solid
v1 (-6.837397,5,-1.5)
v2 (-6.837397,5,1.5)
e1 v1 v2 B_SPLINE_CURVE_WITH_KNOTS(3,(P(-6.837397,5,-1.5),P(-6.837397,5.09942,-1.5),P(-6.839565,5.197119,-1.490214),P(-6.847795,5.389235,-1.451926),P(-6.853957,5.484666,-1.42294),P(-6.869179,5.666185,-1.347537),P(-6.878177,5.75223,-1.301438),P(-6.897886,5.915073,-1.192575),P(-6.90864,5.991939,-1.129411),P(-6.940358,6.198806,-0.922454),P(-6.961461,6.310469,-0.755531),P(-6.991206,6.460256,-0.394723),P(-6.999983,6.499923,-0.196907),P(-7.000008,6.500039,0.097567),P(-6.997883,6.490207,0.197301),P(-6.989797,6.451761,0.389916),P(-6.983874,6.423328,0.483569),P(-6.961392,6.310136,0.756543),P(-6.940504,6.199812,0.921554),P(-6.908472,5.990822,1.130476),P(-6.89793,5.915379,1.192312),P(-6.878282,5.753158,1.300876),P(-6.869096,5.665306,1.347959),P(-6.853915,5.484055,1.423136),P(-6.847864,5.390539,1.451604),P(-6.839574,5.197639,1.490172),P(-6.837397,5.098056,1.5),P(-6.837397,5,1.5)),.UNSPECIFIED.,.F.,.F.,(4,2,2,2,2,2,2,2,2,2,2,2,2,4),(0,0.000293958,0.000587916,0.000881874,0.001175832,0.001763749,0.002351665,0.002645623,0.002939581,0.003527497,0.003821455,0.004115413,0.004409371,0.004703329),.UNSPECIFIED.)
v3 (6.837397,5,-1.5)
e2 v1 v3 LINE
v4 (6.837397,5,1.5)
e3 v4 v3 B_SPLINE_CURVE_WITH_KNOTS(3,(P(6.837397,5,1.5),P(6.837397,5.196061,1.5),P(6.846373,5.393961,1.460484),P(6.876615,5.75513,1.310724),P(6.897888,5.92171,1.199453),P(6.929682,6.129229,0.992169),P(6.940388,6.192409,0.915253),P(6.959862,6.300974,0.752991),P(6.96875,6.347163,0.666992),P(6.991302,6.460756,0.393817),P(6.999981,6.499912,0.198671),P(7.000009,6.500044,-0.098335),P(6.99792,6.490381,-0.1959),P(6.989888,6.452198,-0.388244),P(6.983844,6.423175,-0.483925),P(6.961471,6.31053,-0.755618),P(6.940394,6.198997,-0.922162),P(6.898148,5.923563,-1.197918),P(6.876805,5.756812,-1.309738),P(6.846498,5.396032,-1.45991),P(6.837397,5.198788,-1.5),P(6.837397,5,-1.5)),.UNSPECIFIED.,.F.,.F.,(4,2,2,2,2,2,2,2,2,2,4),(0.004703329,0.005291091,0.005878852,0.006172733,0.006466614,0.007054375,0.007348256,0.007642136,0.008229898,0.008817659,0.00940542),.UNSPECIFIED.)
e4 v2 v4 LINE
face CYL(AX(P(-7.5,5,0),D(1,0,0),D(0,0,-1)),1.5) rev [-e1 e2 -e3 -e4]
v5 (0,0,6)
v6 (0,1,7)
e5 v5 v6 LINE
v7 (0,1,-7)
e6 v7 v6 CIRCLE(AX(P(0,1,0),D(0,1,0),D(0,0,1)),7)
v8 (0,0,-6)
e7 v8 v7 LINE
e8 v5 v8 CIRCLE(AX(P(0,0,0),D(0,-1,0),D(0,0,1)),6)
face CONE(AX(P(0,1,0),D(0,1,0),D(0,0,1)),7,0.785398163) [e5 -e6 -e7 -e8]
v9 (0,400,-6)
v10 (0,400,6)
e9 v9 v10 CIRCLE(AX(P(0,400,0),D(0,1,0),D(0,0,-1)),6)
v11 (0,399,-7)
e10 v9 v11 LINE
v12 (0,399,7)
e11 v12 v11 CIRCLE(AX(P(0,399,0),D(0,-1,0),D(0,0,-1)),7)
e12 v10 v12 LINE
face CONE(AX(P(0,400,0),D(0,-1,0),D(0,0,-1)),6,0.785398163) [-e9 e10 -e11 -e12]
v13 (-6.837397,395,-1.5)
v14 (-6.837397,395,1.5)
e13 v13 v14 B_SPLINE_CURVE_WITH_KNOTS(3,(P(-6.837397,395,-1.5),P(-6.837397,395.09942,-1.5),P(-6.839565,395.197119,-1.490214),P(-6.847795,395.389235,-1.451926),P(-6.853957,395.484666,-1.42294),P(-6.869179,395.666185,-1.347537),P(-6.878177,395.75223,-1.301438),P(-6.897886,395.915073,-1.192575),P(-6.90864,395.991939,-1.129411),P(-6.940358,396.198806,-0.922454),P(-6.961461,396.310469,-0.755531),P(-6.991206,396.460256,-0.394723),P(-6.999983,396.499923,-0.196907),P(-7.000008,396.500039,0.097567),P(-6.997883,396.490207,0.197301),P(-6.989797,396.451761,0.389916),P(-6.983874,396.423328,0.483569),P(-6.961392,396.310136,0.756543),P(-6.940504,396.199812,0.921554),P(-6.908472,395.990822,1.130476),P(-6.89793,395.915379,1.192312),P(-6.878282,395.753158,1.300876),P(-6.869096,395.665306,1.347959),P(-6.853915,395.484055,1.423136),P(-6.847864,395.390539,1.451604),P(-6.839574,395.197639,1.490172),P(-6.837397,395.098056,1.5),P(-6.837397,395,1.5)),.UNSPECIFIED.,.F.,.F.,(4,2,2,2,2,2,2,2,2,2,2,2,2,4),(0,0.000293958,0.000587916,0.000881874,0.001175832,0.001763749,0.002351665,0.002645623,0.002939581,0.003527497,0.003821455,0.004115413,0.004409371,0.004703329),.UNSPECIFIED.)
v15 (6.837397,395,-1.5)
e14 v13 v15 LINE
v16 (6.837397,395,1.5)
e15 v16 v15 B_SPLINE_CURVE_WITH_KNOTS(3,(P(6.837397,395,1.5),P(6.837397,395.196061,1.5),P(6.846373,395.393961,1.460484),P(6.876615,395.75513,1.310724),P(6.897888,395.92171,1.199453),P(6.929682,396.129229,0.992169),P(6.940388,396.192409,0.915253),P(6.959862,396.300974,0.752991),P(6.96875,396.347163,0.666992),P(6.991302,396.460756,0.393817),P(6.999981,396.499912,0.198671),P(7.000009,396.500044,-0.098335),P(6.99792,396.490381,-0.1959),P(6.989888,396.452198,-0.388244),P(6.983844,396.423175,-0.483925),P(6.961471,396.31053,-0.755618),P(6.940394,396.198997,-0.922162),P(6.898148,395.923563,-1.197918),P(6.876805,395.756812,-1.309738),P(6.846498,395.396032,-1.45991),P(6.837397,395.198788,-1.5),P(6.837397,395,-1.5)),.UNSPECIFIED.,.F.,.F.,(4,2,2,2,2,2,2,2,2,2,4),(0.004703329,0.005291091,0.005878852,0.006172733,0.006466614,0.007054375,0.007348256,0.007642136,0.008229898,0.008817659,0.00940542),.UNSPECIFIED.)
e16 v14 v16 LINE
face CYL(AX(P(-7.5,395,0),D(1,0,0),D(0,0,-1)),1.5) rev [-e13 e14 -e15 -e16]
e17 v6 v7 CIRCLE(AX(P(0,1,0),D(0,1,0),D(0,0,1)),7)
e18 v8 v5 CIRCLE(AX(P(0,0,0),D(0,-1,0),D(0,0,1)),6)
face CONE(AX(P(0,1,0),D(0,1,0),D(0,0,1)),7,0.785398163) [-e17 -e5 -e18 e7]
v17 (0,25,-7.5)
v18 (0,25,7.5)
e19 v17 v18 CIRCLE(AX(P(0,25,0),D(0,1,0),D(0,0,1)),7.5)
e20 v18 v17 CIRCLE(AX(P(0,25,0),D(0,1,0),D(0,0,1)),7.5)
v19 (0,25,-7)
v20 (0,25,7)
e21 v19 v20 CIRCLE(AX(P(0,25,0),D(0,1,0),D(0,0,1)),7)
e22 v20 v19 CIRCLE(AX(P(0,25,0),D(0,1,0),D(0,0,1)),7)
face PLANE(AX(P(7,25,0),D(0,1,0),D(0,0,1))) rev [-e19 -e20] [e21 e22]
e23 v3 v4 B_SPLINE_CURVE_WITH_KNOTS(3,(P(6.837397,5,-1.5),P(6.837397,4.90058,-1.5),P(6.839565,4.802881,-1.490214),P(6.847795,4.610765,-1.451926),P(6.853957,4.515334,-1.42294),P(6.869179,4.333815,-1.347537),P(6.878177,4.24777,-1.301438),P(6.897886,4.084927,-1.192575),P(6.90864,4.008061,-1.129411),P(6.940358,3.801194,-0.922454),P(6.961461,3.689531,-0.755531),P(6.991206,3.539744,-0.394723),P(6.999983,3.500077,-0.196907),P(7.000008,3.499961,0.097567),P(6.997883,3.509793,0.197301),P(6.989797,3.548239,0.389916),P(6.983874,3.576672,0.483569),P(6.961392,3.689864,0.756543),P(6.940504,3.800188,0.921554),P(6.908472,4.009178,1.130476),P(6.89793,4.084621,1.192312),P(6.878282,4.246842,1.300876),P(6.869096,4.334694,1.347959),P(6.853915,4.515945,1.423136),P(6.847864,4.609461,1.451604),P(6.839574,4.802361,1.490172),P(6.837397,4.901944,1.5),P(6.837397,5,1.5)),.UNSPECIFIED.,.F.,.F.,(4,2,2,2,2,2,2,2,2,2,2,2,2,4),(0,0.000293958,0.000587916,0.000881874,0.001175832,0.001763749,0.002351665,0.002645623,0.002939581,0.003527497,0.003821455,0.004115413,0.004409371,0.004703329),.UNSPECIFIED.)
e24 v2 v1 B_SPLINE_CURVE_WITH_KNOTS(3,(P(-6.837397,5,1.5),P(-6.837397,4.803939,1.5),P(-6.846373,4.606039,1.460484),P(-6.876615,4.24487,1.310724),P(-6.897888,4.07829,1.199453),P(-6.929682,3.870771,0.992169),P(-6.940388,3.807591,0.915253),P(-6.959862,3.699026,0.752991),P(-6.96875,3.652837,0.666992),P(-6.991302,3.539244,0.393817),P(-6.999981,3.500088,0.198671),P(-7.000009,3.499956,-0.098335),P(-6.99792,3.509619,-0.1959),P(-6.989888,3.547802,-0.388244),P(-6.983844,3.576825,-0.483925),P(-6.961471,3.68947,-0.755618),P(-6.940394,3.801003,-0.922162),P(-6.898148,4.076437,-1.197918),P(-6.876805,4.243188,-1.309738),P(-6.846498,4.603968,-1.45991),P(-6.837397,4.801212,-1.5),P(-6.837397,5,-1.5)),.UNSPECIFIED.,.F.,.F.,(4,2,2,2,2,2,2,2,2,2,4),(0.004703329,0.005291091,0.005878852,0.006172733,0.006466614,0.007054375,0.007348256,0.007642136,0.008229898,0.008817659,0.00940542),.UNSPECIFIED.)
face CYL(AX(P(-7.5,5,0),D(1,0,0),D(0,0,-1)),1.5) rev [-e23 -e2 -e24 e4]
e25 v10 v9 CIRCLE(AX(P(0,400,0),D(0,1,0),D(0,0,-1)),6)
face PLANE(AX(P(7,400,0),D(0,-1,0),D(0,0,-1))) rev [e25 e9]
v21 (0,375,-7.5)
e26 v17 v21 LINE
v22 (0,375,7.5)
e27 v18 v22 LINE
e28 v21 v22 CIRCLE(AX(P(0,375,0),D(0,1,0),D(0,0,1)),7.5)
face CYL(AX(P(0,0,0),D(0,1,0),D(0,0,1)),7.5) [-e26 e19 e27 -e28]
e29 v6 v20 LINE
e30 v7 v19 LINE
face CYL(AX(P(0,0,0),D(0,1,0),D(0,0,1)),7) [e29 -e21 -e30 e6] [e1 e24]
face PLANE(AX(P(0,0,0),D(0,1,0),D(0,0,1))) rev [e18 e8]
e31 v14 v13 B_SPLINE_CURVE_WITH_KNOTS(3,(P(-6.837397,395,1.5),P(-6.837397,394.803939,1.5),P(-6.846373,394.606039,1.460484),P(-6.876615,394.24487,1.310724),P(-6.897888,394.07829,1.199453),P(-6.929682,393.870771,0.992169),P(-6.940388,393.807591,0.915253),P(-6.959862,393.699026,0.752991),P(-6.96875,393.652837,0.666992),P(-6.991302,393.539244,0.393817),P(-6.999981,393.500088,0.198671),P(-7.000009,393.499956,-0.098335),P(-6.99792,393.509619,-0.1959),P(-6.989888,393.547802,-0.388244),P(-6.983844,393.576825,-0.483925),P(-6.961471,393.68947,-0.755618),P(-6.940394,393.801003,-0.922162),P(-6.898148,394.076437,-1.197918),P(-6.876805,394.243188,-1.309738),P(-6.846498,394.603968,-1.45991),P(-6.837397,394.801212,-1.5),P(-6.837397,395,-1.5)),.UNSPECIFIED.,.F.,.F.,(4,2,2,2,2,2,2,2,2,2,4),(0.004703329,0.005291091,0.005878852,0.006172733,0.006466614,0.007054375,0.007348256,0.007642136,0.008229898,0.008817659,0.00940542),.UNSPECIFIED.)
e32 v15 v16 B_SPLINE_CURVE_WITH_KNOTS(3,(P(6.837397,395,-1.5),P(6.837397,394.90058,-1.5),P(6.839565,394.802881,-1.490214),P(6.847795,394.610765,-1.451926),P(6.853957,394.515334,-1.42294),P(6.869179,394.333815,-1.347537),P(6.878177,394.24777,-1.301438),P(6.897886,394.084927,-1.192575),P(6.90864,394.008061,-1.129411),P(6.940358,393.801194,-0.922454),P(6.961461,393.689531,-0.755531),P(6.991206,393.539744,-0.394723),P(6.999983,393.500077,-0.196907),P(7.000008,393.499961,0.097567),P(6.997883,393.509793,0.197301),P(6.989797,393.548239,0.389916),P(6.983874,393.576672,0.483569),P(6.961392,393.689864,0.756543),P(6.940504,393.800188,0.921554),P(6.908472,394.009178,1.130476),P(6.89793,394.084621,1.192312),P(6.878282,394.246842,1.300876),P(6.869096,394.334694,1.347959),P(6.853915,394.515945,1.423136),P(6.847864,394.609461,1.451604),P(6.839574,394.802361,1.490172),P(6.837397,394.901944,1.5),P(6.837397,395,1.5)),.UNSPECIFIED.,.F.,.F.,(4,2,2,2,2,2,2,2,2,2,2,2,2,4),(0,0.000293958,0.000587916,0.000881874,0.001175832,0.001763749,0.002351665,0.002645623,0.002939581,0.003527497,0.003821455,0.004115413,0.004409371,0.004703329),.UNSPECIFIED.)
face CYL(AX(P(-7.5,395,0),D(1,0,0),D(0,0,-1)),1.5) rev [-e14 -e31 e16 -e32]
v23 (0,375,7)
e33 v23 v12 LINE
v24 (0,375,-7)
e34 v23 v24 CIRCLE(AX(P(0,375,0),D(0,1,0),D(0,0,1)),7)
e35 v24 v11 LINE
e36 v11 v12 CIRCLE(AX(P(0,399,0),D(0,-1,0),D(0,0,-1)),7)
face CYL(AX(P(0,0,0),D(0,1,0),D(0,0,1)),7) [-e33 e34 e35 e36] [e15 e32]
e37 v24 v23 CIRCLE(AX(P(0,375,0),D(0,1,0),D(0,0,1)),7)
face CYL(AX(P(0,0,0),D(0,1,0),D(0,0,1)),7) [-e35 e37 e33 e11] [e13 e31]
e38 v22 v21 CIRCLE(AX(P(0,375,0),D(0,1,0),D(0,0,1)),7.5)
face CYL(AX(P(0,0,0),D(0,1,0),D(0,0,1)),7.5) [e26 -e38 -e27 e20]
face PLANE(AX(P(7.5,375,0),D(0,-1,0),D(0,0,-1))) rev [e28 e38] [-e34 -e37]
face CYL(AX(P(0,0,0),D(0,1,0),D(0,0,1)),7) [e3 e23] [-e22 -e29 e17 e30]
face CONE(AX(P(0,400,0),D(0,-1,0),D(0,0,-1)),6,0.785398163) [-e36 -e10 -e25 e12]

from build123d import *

# Parameters (mm, degrees)
CHAMFER1_SIZE           = 1
CUT_EXTRUDE1_DEPTH      = 401.140600289
CUT_EXTRUDE1_DEPTH_BACK = 401.140600289
SKETCH3_R               = 1.5


with BuildPart() as part:
    # Sketch1 → Revolve1 (revolve)
    with BuildSketch(Plane.XY, mode=Mode.PRIVATE) as revolve1_sk:
        Polygon((0, 0), (7, 0), (7, 25), (7.5, 25), (7.5, 375), (7, 375), (7, 400), (0, 400), align=None)
    revolve(revolve1_sk.sketch.rotate(Axis((0, 0, 0), (0, -1, 0)), 90), axis=Axis((0, 0, 0), (0, -1, 0)))

    # Chamfer1
    chamfer1_edges = [part.edges().sort_by_distance(p)[0] for p in [
        (0, 400, -7),
        (0, 0, -7),
    ]]
    chamfer(chamfer1_edges, length=CHAMFER1_SIZE)

    # Sketch3 → Cut-Extrude1 (cut, two sides: drawn at the far end of the back side and taken through both)
    with BuildSketch(Plane(origin=(0, 0, 0), x_dir=(0, 0, -1), z_dir=(1, 0, 0)).offset(-CUT_EXTRUDE1_DEPTH_BACK)):
        with Locations((0, 395)):
            Circle(SKETCH3_R)
        with Locations((0, 5)):
            Circle(SKETCH3_R)
    extrude(amount=CUT_EXTRUDE1_DEPTH + CUT_EXTRUDE1_DEPTH_BACK, mode=Mode.SUBTRACT)


solid = part.part
